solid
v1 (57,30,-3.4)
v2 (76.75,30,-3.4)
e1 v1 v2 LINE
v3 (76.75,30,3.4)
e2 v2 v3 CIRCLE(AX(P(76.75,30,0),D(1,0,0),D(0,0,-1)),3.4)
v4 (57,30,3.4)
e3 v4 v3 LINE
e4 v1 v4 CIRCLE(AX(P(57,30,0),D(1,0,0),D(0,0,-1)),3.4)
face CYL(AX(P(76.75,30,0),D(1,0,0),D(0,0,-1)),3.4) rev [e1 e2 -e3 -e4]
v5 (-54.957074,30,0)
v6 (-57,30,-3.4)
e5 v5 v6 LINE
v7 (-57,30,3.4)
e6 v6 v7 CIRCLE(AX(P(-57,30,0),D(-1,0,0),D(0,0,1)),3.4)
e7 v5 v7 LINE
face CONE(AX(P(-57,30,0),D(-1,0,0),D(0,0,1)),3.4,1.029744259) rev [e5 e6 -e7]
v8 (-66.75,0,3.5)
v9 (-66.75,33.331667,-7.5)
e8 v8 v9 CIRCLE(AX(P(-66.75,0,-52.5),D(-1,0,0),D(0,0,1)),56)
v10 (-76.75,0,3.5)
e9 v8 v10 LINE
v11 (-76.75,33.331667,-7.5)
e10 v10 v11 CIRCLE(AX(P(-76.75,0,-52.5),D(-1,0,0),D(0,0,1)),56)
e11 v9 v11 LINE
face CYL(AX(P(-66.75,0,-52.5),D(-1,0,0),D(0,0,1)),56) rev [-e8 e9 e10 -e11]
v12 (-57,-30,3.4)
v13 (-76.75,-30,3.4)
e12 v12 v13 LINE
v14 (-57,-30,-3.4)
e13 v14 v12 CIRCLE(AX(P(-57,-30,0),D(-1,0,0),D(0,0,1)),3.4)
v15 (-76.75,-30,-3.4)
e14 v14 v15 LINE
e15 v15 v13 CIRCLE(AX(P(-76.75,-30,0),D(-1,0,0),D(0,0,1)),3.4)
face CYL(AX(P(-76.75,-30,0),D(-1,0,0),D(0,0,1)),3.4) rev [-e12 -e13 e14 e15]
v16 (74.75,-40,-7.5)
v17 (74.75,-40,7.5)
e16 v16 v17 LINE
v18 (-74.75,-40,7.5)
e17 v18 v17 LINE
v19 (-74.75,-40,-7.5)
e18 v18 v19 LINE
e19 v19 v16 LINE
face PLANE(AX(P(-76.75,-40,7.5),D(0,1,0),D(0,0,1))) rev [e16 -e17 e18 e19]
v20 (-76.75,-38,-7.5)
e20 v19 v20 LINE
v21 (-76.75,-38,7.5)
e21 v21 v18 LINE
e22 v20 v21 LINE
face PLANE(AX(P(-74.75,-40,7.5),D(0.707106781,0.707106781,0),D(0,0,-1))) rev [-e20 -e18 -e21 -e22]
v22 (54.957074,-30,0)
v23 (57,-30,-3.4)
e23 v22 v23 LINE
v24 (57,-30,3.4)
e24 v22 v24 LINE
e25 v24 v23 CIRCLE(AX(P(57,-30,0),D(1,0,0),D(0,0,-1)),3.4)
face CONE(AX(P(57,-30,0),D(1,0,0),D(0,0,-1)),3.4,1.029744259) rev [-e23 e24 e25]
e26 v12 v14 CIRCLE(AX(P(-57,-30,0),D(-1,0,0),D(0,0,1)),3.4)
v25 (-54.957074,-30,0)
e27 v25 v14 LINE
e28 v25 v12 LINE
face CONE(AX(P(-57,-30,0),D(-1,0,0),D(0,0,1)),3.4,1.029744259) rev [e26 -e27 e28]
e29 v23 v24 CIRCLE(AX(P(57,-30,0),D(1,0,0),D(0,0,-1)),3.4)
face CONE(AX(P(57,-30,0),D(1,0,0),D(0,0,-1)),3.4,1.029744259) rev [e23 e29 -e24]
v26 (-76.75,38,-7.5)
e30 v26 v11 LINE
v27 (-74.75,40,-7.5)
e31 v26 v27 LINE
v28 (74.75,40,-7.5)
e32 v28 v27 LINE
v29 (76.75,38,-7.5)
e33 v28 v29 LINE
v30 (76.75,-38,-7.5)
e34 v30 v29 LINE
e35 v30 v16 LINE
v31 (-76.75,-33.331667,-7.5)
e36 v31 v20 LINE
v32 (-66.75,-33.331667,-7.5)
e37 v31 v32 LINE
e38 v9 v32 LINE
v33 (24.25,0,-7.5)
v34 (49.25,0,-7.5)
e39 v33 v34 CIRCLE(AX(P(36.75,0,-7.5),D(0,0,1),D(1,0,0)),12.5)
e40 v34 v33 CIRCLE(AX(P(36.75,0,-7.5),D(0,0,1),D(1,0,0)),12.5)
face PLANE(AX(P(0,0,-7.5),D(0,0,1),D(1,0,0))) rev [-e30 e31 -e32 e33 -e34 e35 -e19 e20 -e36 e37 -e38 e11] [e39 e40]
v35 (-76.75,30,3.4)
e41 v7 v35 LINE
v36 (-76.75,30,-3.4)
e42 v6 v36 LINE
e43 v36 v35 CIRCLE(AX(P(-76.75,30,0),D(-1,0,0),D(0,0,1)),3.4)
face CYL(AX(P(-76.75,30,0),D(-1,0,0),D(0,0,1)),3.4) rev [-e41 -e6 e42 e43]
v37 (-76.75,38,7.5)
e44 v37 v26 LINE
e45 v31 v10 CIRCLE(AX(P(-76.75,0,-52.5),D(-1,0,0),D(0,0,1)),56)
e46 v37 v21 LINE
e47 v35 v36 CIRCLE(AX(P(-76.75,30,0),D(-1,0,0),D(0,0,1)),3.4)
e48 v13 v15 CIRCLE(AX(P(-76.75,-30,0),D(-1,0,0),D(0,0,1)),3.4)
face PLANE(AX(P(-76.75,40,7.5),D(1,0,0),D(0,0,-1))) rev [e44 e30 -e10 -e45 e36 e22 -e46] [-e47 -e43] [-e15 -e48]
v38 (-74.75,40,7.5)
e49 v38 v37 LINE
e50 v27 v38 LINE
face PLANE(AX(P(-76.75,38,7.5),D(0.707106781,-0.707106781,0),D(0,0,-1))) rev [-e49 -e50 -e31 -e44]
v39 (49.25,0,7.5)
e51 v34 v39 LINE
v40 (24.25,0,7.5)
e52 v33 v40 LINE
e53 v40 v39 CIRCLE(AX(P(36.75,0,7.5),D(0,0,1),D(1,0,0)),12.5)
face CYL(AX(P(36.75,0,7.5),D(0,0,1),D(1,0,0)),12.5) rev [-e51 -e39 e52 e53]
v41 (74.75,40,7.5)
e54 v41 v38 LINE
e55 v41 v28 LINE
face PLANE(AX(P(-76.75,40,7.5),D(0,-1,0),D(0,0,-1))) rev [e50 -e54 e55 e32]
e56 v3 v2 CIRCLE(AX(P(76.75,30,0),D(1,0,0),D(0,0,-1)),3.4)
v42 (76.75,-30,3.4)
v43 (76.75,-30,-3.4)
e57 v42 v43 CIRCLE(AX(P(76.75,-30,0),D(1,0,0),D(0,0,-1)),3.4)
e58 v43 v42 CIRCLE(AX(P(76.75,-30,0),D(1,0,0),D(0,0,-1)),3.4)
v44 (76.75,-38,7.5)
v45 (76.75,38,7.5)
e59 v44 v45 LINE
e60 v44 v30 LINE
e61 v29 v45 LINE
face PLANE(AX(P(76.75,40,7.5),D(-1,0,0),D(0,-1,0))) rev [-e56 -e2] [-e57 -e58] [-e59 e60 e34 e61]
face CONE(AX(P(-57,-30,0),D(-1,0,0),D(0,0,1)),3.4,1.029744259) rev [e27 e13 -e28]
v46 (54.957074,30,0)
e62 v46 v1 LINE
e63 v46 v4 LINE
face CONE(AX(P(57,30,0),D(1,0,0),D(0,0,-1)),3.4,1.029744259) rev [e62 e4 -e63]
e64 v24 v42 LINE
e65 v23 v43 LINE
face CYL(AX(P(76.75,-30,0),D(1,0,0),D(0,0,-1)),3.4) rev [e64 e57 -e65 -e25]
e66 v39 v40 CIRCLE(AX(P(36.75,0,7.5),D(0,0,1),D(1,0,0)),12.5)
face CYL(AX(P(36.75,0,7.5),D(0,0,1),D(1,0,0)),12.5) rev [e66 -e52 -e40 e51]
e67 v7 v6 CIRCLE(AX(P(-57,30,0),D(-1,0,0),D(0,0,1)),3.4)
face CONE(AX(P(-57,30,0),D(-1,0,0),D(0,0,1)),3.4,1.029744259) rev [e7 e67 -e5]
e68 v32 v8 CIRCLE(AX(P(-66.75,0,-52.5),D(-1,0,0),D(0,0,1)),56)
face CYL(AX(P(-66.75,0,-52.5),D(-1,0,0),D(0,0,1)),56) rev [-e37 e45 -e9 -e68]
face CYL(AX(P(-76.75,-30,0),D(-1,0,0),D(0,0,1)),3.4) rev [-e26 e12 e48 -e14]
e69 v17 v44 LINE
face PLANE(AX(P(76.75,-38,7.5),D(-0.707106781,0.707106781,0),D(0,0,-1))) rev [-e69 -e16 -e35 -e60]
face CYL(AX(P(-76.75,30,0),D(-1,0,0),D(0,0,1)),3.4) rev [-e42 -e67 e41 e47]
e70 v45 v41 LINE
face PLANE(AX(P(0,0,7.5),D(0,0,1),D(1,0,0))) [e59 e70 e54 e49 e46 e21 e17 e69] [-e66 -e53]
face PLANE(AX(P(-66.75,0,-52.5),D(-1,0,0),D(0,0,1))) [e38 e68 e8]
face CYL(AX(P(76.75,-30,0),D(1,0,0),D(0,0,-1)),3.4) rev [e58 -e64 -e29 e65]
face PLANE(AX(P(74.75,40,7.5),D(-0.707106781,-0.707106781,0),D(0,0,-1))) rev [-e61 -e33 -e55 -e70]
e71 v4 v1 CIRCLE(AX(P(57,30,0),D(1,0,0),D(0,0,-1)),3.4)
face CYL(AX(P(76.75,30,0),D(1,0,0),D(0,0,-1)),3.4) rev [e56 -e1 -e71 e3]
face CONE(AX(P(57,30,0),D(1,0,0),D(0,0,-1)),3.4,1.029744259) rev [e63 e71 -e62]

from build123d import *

# Parameters (mm, degrees)
SKETCH_1_W                  = 153.5
SKETCH_1_H                  = 80
EXTRUDE_1_DEPTH             = 7.5
HOLE_WIZARD_25_0_25_1_D     = 25
HOLE_WIZARD_M8_1_AT_2_COUNT = 2
HOLE_WIZARD_M8_1_AT_2_PITCH = 60
SKETCH_6_R                  = 56
CUT_EXTRUDE_1_DEPTH         = 10
CHAMFER_1_SIZE              = 2


with BuildPart() as part:
    # 草图1 → 凸台-拉伸1 (new, symmetric)
    with BuildSketch(Plane.XY):
        Rectangle(SKETCH_1_W, SKETCH_1_H)
    extrude(amount=EXTRUDE_1_DEPTH, both=True)

    # Ø25.0 (25) 直径孔1 (through all)
    with Locations(Plane.XY.offset(7.5)):
        with Locations((36.75, 0)):
            Hole(HOLE_WIZARD_25_0_25_1_D / 2)

    # 草图4 → M8 螺纹孔1 (revolve, cut)
    with BuildSketch(Plane(origin=(76.75, -30, 0), x_dir=(0, 0, -1), z_dir=(0, 1, 0))):
        Polygon((0, 0), (0, 21.792926105), (3.4, 19.75), (3.4, 0), align=None)
    hole_wizard_m8_1 = revolve(axis=Axis((83.1, -30, 0), (-1, 0, 0)), mode=Mode.SUBTRACT)

    # M8 螺纹孔1 at 2: M8 螺纹孔1 ×2
    with Locations(*[(0, i * HOLE_WIZARD_M8_1_AT_2_PITCH, 0) for i in range(1, HOLE_WIZARD_M8_1_AT_2_COUNT)]):
        add(hole_wizard_m8_1, mode=Mode.SUBTRACT)

    # 镜向1: M8 螺纹孔1 across plane
    add(hole_wizard_m8_1.mirror(Plane(origin=(0, 0, 0), x_dir=(0, 0, 1), z_dir=(1, 0, 0))), mode=Mode.SUBTRACT)

    # 镜向1 copy 1 sketch → 镜向1 copy 1 (revolve, cut)
    with BuildSketch(Plane(origin=(-76.75, 30, 0), x_dir=(0, 0, -1), z_dir=(0, 1, 0))):
        Polygon((0, 0), (0, -21.792926105), (3.4, -19.75), (3.4, 0), align=None)
    revolve(axis=Axis((-83.1, 30, 0), (-1, 0, 0)), mode=Mode.SUBTRACT)

    # 草图6 → 切除-拉伸1 (cut)
    with BuildSketch(Plane.ZY.offset(76.75)):
        with Locations((-52.5, 0)):
            Circle(SKETCH_6_R)
    extrude(amount=-CUT_EXTRUDE_1_DEPTH, mode=Mode.SUBTRACT)

    # 倒角1
    chamfer_1_edges = [part.edges().sort_by_distance(p)[0] for p in [
        (76.75, -40, 0),
        (-76.75, -40, 0),
        (-76.75, 40, 0),
        (76.75, 40, 0),
    ]]
    chamfer(chamfer_1_edges, length=CHAMFER_1_SIZE)


solid = part.part
